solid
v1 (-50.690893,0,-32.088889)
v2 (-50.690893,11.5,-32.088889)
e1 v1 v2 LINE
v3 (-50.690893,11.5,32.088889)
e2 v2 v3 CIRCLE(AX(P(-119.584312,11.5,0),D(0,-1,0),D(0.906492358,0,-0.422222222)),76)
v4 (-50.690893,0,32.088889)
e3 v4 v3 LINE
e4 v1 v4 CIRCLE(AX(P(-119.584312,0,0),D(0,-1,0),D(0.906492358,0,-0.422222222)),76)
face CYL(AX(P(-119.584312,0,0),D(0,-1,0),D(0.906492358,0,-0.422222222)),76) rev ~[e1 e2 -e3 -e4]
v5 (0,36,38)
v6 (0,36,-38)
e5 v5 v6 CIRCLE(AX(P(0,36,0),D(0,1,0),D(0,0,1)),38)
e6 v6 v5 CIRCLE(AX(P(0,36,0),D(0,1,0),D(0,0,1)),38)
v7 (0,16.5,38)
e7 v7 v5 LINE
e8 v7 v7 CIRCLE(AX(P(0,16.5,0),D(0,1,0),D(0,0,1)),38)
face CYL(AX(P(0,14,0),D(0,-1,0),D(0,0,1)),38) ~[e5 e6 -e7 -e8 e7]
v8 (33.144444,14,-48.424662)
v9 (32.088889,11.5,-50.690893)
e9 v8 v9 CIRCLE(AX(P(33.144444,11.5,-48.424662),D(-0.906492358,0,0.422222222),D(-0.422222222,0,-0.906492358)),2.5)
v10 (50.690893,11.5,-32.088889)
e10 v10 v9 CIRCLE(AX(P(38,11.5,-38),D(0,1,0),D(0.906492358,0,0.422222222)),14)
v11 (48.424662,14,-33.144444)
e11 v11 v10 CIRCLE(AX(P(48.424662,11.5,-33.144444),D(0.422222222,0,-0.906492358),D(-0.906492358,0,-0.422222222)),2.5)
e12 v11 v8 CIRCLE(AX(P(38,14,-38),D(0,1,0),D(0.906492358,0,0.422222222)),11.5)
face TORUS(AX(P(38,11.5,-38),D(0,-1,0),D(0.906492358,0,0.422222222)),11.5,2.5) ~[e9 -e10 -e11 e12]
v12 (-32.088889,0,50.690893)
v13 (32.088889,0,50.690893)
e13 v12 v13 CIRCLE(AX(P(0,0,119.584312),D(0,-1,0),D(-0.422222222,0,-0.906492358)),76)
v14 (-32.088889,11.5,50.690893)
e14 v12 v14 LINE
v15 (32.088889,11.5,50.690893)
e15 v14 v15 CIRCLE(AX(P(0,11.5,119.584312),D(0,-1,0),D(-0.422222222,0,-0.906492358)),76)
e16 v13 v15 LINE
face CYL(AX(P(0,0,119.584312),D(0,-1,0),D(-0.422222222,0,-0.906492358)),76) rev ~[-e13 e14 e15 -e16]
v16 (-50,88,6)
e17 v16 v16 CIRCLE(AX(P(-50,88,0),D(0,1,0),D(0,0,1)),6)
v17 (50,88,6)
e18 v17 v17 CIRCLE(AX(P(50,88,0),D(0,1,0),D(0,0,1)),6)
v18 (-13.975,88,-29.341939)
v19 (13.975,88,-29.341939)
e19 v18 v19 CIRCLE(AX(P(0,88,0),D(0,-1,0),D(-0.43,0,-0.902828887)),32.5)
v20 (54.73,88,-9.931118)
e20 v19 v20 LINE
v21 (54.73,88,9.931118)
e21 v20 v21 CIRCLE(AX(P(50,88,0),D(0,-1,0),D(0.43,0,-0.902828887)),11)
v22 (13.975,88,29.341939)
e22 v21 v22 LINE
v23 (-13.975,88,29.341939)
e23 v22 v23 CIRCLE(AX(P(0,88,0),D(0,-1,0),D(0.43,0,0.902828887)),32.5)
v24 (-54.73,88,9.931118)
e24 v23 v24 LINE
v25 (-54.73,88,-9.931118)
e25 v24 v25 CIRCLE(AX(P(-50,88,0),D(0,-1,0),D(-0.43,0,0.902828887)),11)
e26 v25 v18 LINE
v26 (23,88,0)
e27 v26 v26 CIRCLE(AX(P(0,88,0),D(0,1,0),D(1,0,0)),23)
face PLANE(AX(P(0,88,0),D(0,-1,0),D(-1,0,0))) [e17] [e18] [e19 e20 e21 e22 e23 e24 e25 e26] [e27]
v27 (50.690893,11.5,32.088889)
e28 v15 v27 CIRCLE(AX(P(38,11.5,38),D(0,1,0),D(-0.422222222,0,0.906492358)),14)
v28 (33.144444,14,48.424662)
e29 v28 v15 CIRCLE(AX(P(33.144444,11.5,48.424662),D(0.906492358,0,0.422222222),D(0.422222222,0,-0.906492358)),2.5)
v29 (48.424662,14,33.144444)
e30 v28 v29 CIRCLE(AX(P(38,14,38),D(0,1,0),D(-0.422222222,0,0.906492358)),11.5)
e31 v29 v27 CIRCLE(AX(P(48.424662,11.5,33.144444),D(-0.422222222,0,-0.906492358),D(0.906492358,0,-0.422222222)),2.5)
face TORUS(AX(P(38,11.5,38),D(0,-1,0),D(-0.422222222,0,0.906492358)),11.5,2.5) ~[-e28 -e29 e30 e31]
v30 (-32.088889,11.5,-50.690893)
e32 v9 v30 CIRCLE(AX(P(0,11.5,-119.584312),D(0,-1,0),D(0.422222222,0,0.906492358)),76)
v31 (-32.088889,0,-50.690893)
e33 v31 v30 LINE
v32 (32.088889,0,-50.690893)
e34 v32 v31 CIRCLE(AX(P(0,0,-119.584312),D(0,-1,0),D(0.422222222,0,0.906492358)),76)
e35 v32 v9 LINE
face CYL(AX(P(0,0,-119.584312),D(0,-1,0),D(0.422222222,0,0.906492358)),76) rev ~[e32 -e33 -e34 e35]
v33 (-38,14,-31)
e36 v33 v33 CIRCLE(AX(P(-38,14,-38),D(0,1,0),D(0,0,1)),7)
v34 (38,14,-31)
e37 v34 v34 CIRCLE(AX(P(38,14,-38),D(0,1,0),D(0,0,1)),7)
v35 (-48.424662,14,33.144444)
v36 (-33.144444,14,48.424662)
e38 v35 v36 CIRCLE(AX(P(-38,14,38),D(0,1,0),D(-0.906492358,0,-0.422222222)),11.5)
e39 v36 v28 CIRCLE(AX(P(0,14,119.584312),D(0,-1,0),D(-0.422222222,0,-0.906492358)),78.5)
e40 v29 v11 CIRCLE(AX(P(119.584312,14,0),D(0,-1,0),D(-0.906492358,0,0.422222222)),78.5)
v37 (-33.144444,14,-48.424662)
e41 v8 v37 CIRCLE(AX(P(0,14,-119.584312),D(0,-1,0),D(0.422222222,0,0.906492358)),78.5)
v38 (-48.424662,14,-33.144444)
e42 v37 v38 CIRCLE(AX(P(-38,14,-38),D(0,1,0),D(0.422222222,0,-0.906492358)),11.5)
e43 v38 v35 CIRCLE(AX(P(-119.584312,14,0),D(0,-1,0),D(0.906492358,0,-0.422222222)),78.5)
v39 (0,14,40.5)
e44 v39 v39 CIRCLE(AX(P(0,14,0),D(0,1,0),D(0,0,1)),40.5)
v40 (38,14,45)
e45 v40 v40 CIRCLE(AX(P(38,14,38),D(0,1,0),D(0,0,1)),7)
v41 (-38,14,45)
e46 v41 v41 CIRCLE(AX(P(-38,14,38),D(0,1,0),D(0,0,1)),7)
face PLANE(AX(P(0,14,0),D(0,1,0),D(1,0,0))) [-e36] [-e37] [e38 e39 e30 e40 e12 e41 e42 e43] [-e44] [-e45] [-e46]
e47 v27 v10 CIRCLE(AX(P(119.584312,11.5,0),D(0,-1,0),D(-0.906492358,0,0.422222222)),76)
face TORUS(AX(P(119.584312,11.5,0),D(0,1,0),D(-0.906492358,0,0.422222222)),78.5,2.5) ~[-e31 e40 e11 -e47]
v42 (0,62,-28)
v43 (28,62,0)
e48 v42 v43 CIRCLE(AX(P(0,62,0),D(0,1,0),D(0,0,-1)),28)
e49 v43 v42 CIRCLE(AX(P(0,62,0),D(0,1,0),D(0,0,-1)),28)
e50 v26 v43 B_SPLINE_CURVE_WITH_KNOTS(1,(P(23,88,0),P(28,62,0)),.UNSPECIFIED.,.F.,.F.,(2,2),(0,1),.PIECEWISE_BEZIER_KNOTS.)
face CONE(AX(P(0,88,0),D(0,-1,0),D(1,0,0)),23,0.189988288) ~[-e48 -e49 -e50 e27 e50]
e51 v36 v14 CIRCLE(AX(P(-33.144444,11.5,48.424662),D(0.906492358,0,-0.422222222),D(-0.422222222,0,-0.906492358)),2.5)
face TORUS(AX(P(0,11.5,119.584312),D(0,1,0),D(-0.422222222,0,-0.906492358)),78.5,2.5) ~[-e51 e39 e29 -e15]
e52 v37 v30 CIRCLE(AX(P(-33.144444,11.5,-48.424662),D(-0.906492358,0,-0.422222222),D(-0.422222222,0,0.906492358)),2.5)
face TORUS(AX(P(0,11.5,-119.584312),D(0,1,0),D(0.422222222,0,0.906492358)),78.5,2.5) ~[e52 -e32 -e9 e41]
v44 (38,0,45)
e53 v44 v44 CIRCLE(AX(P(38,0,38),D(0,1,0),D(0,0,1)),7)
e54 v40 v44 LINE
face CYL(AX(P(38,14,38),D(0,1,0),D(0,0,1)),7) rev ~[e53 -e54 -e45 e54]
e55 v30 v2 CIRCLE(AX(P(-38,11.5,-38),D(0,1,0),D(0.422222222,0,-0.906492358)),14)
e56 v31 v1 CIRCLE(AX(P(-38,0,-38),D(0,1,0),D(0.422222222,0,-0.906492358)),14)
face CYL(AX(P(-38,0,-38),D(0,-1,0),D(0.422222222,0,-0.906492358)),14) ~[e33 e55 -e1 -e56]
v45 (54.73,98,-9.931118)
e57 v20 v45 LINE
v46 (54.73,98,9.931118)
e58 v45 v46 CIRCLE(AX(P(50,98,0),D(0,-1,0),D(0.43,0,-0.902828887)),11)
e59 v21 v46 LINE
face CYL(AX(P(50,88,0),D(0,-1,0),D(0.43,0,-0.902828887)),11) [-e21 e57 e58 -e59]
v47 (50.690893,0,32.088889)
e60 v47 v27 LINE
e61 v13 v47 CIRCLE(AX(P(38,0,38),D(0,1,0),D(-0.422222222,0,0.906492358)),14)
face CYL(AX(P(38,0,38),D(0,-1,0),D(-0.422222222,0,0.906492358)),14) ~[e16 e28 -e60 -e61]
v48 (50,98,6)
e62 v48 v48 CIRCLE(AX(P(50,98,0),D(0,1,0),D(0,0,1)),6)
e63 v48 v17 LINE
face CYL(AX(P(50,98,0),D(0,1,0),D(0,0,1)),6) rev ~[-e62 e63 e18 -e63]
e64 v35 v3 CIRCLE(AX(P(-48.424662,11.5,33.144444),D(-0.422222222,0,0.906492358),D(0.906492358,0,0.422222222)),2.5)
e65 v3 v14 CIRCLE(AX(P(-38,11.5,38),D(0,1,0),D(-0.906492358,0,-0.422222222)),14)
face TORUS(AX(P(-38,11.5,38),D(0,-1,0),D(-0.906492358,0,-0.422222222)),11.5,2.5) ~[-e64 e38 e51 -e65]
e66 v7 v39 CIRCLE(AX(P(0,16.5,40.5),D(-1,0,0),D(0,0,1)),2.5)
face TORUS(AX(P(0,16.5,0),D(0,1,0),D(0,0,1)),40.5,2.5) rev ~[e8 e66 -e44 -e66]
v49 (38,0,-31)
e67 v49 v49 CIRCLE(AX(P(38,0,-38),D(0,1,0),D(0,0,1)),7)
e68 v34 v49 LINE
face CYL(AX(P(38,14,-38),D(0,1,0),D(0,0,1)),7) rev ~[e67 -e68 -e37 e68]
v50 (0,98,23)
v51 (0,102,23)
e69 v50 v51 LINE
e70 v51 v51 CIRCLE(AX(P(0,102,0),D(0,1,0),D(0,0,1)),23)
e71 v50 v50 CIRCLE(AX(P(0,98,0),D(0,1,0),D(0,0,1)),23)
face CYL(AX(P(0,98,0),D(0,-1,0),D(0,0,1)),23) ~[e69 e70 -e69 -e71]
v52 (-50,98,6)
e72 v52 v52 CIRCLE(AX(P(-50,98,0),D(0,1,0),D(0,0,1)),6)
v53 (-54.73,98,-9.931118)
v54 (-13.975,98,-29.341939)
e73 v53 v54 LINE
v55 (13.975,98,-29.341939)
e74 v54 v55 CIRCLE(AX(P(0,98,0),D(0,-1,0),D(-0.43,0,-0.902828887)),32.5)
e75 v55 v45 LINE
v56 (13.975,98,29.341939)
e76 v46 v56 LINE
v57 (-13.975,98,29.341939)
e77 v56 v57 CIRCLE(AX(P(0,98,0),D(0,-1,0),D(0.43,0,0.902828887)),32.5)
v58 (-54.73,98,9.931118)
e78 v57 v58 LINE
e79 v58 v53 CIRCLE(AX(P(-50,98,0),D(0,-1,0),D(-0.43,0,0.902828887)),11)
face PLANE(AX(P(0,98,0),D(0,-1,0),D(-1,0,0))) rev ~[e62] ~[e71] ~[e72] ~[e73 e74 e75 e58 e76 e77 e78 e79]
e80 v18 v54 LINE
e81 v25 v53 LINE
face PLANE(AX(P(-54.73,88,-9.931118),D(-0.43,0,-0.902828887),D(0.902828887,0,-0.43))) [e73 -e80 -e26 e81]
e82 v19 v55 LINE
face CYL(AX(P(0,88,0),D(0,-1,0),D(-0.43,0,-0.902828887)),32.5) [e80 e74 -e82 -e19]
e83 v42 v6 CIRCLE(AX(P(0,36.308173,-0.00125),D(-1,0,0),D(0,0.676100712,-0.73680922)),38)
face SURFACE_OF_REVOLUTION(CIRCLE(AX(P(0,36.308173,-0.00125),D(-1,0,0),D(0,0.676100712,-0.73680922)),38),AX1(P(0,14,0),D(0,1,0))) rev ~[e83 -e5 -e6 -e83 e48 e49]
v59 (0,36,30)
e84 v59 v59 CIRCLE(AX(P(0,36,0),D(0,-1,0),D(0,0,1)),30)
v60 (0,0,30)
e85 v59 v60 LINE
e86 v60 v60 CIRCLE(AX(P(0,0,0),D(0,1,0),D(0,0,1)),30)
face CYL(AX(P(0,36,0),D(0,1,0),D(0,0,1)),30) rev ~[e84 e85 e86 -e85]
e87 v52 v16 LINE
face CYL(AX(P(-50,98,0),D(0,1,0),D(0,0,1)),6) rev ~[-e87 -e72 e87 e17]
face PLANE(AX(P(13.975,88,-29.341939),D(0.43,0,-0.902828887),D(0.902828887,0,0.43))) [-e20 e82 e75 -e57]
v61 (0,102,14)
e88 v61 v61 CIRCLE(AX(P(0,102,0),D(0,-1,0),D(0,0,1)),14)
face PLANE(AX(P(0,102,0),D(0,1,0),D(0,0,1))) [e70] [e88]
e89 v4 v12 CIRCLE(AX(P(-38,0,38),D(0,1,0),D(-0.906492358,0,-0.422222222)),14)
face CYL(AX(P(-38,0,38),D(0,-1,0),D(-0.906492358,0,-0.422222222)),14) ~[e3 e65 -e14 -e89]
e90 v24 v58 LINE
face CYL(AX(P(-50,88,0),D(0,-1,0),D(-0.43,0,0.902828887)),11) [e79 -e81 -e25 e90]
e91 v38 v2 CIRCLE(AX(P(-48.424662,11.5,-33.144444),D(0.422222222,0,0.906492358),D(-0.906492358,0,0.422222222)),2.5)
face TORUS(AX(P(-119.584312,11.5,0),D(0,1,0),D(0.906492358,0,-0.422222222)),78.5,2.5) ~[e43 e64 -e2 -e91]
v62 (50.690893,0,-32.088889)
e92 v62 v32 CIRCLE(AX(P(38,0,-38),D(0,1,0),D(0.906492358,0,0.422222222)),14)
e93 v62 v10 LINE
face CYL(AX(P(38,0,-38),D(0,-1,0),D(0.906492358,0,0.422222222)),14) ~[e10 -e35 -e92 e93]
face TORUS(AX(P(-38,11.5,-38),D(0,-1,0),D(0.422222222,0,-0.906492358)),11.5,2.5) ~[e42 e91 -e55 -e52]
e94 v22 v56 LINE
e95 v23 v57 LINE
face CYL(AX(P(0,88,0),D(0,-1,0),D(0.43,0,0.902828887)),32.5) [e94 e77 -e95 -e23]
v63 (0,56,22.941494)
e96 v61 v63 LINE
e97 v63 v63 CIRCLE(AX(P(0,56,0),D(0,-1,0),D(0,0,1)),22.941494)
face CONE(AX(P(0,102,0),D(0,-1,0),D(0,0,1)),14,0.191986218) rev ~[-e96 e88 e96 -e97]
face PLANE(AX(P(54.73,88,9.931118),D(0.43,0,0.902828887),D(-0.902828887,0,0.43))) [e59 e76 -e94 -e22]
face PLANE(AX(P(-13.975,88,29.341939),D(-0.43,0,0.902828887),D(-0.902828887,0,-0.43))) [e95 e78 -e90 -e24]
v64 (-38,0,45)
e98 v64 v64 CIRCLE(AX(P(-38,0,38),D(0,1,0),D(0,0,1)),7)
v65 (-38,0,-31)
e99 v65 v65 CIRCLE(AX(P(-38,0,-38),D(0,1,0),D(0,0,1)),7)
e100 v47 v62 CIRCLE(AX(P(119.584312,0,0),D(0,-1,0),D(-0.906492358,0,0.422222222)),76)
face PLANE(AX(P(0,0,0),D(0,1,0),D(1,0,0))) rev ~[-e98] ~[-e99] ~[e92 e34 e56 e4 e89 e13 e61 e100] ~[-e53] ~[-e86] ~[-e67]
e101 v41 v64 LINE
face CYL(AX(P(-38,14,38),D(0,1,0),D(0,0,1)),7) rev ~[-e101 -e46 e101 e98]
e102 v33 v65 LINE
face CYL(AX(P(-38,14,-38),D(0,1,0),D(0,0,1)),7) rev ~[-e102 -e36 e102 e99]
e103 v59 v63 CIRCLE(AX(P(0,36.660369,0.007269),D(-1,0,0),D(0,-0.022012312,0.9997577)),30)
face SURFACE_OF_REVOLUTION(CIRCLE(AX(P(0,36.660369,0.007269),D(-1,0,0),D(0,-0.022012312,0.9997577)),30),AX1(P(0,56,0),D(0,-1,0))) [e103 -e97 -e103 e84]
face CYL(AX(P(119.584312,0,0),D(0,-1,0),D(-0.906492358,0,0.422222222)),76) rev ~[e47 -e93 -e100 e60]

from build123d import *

# Parameters (mm, degrees)
BASE_FLANGE_DEPTH               = 14
BASE_BOSS_SKETCH_R              = 38
BASE_BOSS_76_DEPTH              = 22
NECK_LOFT_UPPER_PROFILE_46_R    = 23
NECK_LOFT_LOWER_PROFILE_R       = 28
TOP_FLANGE_DEPTH                = 10
TOP_SPIGOT_SKETCH_R             = 23
TOP_SPIGOT_46_DEPTH             = 4
BOTTOM_BORE_SKETCH_R            = 30
BOTTOM_BORE_60_DEPTH            = 104.831594421
BASE_MOUNTING_HOLES_SKETCH_R    = 7
BASE_MOUNTING_HOLES_4X_14_DEPTH = 120.033608699
TOP_FLANGE_HOLES_2X_12_REACH    = 128.606
TOP_FLANGE_HOLES_SKETCH_R       = 6
BASE_BOSS_FILLET_R2_5_R         = 2.5


with BuildPart() as part:
    # Base Flange Sketch → Base Flange (new body)
    with BuildSketch(Plane(origin=(0, 0, 0), x_dir=(1, 0, 0), z_dir=(0, 1, 0))):
        with BuildLine():
            ThreePointArc((-32.088888889, 50.690893012), (-47.899494937, 47.899494937), (-50.690893012, 32.088888889))
            ThreePointArc((-50.690893012, 32.088888889), (-43.584312217, 0), (-50.690893012, -32.088888889))
            ThreePointArc((-50.690893012, -32.088888889), (-47.899494937, -47.899494937), (-32.088888889, -50.690893012))
            ThreePointArc((-32.088888889, -50.690893012), (0, -43.584312217), (32.088888889, -50.690893012))
            ThreePointArc((32.088888889, -50.690893012), (47.899494937, -47.899494937), (50.690893012, -32.088888889))
            ThreePointArc((50.690893012, -32.088888889), (43.584312217, 0), (50.690893012, 32.088888889))
            ThreePointArc((50.690893012, 32.088888889), (47.899494937, 47.899494937), (32.088888889, 50.690893012))
            ThreePointArc((32.088888889, 50.690893012), (0, 43.584312217), (-32.088888889, 50.690893012))
        make_face()
    extrude(amount=BASE_FLANGE_DEPTH)

    # Base Boss Sketch → Base Boss Ø76 (add)
    with BuildSketch(Plane(origin=(0, 14, 0), x_dir=(1, 0, 0), z_dir=(0, 1, 0))):
        with Locations(Location((0, 0, 0), (0, 0, 270))):
            Circle(BASE_BOSS_SKETCH_R)
    extrude(amount=BASE_BOSS_76_DEPTH)

    # Ball Body Profile → Ball Body (revolve)
    with BuildSketch(Plane(origin=(0, 0, 0), x_dir=(0, 0, -1), z_dir=(1, 0, 0)), mode=Mode.PRIVATE) as ball_body_sk:
        with BuildLine():
            Line((0, 62), (-28, 62))
            ThreePointArc((-28, 62), (-35.468382669, 49.94937795), (-38, 36))
            Line((-38, 36), (0, 36))
            Line((0, 36), (0, 62))
        make_face()
    revolve(ball_body_sk.sketch.rotate(Axis((0, 14, 0), (0, 1, 0)), 180), axis=Axis((0, 14, 0), (0, 1, 0)))

    # Neck Loft Upper Profile Ø46 → Neck Loft section 0
    with BuildSketch(Plane(origin=(0, 88, 0), x_dir=(1, 0, 0), z_dir=(0, 1, 0))):
        Circle(NECK_LOFT_UPPER_PROFILE_46_R)
    # Neck Loft Lower Profile → Neck Loft section 1
    with BuildSketch(Plane(origin=(0, 62, 0), x_dir=(1, 0, 0), z_dir=(0, 1, 0))):
        Circle(NECK_LOFT_LOWER_PROFILE_R)
    loft()

    # Top Flange Sketch → Top Flange (add)
    with BuildSketch(Plane(origin=(0, 88, 0), x_dir=(1, 0, 0), z_dir=(0, 1, 0))):
        with BuildLine():
            Line((-54.73, 9.931117762), (-13.975, 29.341938842))
            ThreePointArc((-13.975, 29.341938842), (0, 32.5), (13.975, 29.341938842))
            Line((13.975, 29.341938842), (54.73, 9.931117762))
            ThreePointArc((54.73, 9.931117762), (61, 0), (54.73, -9.931117762))
            Line((54.73, -9.931117762), (13.975, -29.341938842))
            ThreePointArc((13.975, -29.341938842), (0, -32.5), (-13.975, -29.341938842))
            Line((-13.975, -29.341938842), (-54.73, -9.931117762))
            ThreePointArc((-54.73, -9.931117762), (-61, 0), (-54.73, 9.931117762))
        make_face()
    extrude(amount=TOP_FLANGE_DEPTH)

    # Top Spigot Sketch → Top Spigot Ø46 (add)
    with BuildSketch(Plane(origin=(0, 98, 0), x_dir=(1, 0, 0), z_dir=(0, 1, 0))):
        with Locations(Location((0, 0, 0), (0, 0, 270))):
            Circle(TOP_SPIGOT_SKETCH_R)
    extrude(amount=TOP_SPIGOT_46_DEPTH)

    # Ball Groove Profile → Ball Groove (revolve, cut)
    with BuildSketch(Plane.XY, mode=Mode.PRIVATE) as ball_groove_sk:
        Polygon((0, 102), (14, 102), (22.94149422, 56), (0, 56), align=None)
    revolve(ball_groove_sk.sketch.rotate(Axis((0, 102, 0), (0, -1, 0)), 90), axis=Axis((0, 102, 0), (0, -1, 0)), mode=Mode.SUBTRACT)

    # Inner Cavity Profile → Inner Cavity (revolve, cut)
    with BuildSketch(Plane.XY, mode=Mode.PRIVATE) as inner_cavity_sk:
        with BuildLine():
            Line((0, 36), (30, 36))
            ThreePointArc((30, 36), (28.297120073, 46.644573206), (22.94149422, 56))
            Line((22.94149422, 56), (0, 56))
            Line((0, 56), (0, 36))
        make_face()
    revolve(inner_cavity_sk.sketch.rotate(Axis((0, 56, 0), (0, -1, 0)), 90), axis=Axis((0, 56, 0), (0, -1, 0)), mode=Mode.SUBTRACT)

    # Bottom Bore Sketch → Bottom Bore Ø60 (cut, through all)
    with BuildSketch(Plane(origin=(0, 36, 0), x_dir=(1, 0, 0), z_dir=(0, 1, 0))):
        with Locations(Location((0, 0, 0), (0, 0, 270))):
            Circle(BOTTOM_BORE_SKETCH_R)
    extrude(amount=-BOTTOM_BORE_60_DEPTH, mode=Mode.SUBTRACT)

    # Base Mounting Holes Sketch → Base Mounting Holes 4xØ14 (cut, through all)
    with BuildSketch(Plane(origin=(0, 14, 0), x_dir=(1, 0, 0), z_dir=(0, 1, 0))):
        with Locations(Location((38, 38, 0), (0, 0, 270))):
            Circle(BASE_MOUNTING_HOLES_SKETCH_R)
        with Locations(Location((38, -38, 0), (0, 0, 270))):
            Circle(BASE_MOUNTING_HOLES_SKETCH_R)
        with Locations(Location((-38, 38, 0), (0, 0, 270))):
            Circle(BASE_MOUNTING_HOLES_SKETCH_R)
        with Locations(Location((-38, -38, 0), (0, 0, 270))):
            Circle(BASE_MOUNTING_HOLES_SKETCH_R)
    extrude(amount=-BASE_MOUNTING_HOLES_4X_14_DEPTH, mode=Mode.SUBTRACT)

    # Top Flange Holes Sketch → Top Flange Holes 2xØ12 (cut, up to next)
    with BuildSketch(Plane(origin=(0, 98, 0), x_dir=(1, 0, 0), z_dir=(0, 1, 0)), mode=Mode.PRIVATE) as top_flange_holes_2x_12_sk1:
        with Locations(Location((50, 0, 0), (0, 0, 270))):
            Circle(TOP_FLANGE_HOLES_SKETCH_R)
    top_flange_holes_2x_12_tool1 = extrude(top_flange_holes_2x_12_sk1.sketch, amount=-TOP_FLANGE_HOLES_2X_12_REACH, mode=Mode.PRIVATE) & part.part
    # Top Flange Holes Sketch → Top Flange Holes 2xØ12 (cut, up to next)
    with BuildSketch(Plane(origin=(0, 98, 0), x_dir=(1, 0, 0), z_dir=(0, 1, 0)), mode=Mode.PRIVATE) as top_flange_holes_2x_12_sk2:
        with Locations(Location((-50, 0, 0), (0, 0, 270))):
            Circle(TOP_FLANGE_HOLES_SKETCH_R)
    top_flange_holes_2x_12_tool2 = extrude(top_flange_holes_2x_12_sk2.sketch, amount=-TOP_FLANGE_HOLES_2X_12_REACH, mode=Mode.PRIVATE) & part.part
    add(top_flange_holes_2x_12_tool1.solids().sort_by_distance((50, 98, 0))[0], mode=Mode.SUBTRACT)
    add(top_flange_holes_2x_12_tool2.solids().sort_by_distance((-50, 98, 0))[0], mode=Mode.SUBTRACT)

    # Base Boss Fillet R2.5
    base_boss_fillet_r2_5_edges = [part.edges().sort_by_distance(p)[0] for p in [
        (0, 14, 43.584312217),
        (47.899494937, 14, 47.899494937),
        (43.584312217, 14, 0),
        (47.899494937, 14, -47.899494937),
        (0, 14, -38),
        (0, 14, -43.584312217),
        (-47.899494937, 14, -47.899494937),
        (-43.584312217, 14, 0),
        (-47.899494937, 14, 47.899494937),
    ]]
    fillet(base_boss_fillet_r2_5_edges, radius=BASE_BOSS_FILLET_R2_5_R)


solid = part.part
